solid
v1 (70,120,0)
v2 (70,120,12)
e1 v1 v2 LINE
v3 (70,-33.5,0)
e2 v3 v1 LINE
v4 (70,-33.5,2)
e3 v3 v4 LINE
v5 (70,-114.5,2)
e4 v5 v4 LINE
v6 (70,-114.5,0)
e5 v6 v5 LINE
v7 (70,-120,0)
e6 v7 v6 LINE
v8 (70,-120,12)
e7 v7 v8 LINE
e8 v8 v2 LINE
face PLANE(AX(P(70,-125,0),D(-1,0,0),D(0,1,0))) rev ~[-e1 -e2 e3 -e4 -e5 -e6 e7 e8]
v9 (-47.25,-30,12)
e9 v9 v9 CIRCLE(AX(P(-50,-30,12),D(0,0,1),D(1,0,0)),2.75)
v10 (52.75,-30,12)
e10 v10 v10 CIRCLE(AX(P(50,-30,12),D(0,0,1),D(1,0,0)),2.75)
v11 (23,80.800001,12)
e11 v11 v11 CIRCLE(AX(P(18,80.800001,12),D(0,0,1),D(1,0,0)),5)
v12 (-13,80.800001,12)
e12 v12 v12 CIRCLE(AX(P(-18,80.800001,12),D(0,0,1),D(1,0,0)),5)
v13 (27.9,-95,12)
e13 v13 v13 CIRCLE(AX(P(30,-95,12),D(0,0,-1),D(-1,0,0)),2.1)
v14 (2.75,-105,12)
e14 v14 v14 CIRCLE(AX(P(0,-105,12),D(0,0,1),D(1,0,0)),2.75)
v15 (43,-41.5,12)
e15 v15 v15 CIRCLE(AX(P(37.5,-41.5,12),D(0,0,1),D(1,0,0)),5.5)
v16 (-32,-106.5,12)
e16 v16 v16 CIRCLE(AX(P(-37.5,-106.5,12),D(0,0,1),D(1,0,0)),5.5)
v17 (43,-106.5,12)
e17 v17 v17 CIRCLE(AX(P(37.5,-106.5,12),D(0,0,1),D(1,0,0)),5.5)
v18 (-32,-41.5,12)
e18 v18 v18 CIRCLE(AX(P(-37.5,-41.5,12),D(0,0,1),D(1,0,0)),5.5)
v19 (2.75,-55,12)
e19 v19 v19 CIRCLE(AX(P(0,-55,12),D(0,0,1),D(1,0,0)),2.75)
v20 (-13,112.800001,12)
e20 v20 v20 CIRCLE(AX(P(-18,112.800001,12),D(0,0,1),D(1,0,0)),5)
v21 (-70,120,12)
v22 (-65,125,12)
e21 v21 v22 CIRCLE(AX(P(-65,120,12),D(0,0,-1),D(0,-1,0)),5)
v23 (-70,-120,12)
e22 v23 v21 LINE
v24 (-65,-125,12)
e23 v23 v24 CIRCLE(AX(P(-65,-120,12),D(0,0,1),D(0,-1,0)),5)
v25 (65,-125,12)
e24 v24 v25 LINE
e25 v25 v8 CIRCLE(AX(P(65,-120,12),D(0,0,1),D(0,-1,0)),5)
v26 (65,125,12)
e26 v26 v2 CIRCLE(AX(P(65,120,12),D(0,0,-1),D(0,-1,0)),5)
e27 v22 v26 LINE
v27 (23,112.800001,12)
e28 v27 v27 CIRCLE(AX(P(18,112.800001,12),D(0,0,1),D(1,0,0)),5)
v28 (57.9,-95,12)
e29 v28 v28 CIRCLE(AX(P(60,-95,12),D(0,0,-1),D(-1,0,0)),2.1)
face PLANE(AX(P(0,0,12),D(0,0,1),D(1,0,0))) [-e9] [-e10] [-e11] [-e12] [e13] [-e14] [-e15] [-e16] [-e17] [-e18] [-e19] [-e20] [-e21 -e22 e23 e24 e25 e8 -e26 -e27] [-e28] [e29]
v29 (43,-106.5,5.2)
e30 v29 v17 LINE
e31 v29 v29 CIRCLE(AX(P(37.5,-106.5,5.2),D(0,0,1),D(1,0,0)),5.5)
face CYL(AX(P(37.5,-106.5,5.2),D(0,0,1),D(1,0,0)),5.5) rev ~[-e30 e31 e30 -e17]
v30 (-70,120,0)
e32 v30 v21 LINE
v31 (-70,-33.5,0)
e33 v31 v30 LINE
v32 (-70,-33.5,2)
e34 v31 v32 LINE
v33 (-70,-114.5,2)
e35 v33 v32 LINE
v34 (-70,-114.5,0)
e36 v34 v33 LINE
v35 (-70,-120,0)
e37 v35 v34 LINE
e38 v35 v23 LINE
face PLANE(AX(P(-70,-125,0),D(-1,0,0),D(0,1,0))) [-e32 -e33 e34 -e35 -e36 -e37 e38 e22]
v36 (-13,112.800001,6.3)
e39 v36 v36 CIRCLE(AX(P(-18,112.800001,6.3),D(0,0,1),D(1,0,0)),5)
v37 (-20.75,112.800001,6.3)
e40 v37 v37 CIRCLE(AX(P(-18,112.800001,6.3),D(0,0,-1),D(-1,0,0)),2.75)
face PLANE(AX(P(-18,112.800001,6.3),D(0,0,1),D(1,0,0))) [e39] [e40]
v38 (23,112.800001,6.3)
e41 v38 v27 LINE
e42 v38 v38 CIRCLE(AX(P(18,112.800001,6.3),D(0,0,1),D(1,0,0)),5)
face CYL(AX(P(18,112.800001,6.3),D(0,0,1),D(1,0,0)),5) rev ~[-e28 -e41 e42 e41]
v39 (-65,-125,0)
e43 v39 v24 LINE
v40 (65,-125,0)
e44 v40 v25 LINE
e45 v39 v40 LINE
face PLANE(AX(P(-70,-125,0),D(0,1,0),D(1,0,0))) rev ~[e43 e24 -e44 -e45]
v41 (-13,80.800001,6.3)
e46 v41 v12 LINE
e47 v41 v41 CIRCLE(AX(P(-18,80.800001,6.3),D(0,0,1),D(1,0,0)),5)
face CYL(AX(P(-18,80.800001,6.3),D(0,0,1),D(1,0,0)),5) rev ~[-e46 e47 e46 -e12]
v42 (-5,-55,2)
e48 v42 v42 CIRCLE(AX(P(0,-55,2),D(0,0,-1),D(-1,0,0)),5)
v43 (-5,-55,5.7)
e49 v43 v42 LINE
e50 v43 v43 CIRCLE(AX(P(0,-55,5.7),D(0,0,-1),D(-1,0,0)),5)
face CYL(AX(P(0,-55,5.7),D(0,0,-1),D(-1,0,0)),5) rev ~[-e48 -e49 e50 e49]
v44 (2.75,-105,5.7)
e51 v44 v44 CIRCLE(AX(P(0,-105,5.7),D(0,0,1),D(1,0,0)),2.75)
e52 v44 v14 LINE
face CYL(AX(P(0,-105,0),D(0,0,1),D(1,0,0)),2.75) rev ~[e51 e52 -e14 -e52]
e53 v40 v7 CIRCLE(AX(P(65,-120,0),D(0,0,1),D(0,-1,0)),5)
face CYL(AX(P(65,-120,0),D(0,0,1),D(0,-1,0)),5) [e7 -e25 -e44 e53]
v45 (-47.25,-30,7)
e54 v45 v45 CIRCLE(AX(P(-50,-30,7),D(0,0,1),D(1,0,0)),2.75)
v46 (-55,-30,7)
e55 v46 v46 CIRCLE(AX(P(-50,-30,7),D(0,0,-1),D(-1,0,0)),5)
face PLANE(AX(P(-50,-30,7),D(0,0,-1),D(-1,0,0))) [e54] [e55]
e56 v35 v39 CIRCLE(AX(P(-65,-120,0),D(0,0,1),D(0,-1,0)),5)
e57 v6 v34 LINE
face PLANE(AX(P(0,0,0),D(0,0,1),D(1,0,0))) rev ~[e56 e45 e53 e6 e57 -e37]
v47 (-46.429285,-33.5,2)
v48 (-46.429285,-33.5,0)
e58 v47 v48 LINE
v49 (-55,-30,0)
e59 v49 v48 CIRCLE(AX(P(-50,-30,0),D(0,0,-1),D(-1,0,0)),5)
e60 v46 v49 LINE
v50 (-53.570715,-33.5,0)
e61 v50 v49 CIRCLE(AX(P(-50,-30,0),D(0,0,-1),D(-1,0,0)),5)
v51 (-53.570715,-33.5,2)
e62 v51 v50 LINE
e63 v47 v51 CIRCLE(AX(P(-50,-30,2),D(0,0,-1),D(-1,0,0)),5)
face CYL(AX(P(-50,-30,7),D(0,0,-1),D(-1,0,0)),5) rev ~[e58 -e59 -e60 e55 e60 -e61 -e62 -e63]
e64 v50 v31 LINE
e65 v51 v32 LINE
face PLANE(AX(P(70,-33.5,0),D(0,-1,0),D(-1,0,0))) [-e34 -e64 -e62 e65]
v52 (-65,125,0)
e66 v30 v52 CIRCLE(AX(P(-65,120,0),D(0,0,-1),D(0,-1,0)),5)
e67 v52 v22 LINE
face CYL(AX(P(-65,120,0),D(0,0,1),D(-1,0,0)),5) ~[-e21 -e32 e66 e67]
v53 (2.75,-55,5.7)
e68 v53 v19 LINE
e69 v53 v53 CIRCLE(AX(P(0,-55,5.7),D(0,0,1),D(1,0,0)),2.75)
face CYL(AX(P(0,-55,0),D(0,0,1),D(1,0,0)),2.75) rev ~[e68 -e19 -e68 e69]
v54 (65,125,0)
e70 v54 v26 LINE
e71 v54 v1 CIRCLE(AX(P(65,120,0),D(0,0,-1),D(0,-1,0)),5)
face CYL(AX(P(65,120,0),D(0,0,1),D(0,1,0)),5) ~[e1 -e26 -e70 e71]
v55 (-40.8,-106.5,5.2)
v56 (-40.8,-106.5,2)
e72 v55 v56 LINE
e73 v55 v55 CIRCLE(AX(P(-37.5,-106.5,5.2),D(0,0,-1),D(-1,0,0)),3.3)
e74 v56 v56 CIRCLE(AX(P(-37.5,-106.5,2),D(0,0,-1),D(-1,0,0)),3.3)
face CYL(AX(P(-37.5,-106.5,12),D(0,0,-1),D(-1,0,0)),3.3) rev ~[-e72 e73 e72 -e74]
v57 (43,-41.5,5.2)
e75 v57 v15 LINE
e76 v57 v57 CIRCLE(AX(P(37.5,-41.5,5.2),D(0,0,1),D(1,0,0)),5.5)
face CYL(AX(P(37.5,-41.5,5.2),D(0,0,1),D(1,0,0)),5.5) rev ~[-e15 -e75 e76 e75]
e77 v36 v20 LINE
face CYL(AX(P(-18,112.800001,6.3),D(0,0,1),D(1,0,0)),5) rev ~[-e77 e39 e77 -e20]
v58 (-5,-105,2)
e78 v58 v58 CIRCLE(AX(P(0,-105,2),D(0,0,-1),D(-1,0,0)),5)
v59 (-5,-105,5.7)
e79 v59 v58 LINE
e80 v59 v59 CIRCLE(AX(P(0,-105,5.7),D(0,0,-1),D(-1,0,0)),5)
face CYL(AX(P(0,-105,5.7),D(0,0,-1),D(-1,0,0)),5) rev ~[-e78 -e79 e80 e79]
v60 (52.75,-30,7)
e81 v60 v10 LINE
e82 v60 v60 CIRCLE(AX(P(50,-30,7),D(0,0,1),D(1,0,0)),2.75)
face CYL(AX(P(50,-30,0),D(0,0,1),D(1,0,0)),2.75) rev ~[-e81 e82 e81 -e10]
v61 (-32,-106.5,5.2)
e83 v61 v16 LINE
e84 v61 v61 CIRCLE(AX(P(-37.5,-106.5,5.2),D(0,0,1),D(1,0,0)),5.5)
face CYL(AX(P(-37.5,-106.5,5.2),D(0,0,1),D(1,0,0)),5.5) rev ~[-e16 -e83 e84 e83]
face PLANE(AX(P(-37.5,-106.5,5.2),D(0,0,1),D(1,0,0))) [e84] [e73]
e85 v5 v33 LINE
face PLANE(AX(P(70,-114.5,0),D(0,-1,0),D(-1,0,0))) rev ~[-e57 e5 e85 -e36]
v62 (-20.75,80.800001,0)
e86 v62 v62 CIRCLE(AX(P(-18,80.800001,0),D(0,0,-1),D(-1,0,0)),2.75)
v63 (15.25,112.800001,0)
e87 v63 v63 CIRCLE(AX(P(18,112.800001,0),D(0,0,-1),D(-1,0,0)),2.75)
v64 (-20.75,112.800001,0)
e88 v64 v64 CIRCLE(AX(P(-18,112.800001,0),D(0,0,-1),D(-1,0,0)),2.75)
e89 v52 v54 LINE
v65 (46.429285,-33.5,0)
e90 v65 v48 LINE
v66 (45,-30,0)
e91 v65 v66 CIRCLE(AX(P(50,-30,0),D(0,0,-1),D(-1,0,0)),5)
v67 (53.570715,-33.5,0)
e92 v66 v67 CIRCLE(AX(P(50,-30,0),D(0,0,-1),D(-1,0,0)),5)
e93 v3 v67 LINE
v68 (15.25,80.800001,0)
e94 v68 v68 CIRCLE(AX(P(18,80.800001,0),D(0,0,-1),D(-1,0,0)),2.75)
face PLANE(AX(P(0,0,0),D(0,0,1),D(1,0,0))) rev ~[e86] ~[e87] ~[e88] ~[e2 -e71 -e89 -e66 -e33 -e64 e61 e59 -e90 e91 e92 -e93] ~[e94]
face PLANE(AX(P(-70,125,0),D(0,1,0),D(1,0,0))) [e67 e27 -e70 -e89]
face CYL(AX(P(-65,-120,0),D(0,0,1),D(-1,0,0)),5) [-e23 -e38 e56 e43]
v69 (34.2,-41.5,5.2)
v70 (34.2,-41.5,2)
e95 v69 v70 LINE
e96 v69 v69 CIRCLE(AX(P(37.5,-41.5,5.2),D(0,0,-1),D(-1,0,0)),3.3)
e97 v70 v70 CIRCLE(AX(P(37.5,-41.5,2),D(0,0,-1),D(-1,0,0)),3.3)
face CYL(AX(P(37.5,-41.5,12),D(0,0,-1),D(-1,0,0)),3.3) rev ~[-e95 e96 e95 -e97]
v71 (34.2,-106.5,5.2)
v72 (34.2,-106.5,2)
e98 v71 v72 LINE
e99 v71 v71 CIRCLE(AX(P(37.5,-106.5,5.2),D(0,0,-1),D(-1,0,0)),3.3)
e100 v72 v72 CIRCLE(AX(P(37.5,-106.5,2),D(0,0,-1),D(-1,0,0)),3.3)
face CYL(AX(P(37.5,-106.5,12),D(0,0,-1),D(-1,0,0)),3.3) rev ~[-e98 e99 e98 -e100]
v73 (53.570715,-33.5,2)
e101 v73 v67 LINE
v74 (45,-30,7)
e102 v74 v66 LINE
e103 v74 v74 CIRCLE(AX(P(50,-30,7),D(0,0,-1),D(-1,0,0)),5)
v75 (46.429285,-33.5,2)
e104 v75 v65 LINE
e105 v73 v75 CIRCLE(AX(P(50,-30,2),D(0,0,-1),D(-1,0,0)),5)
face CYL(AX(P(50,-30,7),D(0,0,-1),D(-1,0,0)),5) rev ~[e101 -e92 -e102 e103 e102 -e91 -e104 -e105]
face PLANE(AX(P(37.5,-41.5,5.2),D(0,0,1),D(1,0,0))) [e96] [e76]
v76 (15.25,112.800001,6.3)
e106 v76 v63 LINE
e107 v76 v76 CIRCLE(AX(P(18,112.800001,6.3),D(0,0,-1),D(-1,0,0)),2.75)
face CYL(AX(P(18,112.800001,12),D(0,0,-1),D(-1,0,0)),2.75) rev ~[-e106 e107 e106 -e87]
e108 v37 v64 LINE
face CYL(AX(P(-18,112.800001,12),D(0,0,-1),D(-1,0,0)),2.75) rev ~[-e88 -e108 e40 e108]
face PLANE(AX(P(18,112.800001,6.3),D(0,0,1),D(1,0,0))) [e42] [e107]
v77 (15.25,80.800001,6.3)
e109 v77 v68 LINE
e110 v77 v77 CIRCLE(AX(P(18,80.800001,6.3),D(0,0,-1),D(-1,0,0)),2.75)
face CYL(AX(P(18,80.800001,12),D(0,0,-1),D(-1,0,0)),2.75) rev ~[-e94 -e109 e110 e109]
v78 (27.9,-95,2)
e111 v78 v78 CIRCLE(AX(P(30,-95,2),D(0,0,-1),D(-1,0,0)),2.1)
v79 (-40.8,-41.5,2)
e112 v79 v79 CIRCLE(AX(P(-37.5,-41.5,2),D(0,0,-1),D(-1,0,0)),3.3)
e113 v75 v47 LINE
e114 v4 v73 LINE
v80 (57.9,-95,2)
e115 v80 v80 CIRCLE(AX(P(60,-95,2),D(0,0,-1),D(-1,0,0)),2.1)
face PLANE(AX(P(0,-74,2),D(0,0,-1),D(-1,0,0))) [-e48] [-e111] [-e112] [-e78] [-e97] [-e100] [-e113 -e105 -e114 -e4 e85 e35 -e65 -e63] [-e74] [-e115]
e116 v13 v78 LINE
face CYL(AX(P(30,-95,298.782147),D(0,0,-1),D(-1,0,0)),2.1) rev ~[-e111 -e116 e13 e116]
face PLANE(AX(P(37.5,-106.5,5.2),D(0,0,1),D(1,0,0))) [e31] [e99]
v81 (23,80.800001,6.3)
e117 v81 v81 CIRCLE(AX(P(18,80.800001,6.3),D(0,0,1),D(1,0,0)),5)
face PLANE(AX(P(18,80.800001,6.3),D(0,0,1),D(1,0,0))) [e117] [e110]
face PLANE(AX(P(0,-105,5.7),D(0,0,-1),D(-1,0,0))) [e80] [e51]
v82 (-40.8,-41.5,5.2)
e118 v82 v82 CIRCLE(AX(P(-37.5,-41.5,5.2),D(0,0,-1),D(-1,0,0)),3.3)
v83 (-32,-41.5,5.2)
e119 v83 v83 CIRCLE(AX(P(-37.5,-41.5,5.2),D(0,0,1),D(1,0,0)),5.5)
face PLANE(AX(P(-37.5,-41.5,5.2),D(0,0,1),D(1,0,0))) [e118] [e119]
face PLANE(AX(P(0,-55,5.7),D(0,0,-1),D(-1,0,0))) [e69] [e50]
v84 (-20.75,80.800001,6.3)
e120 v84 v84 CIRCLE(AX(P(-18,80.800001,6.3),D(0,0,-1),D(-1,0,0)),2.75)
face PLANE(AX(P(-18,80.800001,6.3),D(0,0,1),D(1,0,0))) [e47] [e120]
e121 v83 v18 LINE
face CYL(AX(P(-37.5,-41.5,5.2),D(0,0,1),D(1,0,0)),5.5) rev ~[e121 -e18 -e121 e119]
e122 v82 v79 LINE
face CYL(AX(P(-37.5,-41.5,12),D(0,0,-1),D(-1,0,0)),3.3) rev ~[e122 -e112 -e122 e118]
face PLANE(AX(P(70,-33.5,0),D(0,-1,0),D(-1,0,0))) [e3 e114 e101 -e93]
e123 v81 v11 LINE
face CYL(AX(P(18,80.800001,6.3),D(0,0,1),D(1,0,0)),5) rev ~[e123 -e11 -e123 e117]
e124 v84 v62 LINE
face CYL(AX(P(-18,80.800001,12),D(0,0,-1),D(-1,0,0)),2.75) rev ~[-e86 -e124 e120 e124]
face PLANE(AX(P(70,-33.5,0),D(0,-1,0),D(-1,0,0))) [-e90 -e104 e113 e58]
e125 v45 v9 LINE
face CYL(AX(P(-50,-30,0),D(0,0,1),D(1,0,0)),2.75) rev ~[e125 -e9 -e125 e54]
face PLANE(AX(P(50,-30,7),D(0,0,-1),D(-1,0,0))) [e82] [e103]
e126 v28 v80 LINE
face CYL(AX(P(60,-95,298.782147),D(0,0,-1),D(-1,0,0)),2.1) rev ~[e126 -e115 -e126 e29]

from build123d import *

# Parameters (mm, degrees)
SKETCH_1_W                = 140
SKETCH_1_H                = 250
EXTRUDE_1_DEPTH           = 12
HOLE_WIZARD_1_D           = 5.5
HOLE_WIZARD_1_DEPTH       = 15
HOLE_WIZARD_1_CBORE_D     = 10
HOLE_WIZARD_1_CBORE_DEPTH = 5.7
HOLE_WIZARD_1_TIP         = 1.652366702
HOLE_WIZARD_2_D           = 6.6
HOLE_WIZARD_2_DEPTH       = 15
HOLE_WIZARD_2_CBORE_D     = 11
HOLE_WIZARD_2_CBORE_DEPTH = 6.8
HOLE_WIZARD_2_TIP         = 1.982840043
HOLE_WIZARD_3_D           = 5.5
HOLE_WIZARD_3_DEPTH       = 14.4
HOLE_WIZARD_3_CBORE_D     = 10
HOLE_WIZARD_3_CBORE_DEPTH = 5.7
HOLE_WIZARD_3_TIP         = 1.652366702
SKETCH_8_W                = 140
SKETCH_8_H                = 81
CUT_EXTRUDE_1_DEPTH       = 2
HOLE_WIZARD_0_D           = 5.5
HOLE_WIZARD_0_CBORE_D     = 10
HOLE_WIZARD_0_CBORE_DEPTH = 7
HOLE_WIZARD_M5_1_D        = 4.2
FILLET_1_R                = 5


with BuildPart() as part:
    # 草图1 → 凸台-拉伸1 (new body)
    with BuildSketch(Plane.XY):
        Rectangle(SKETCH_1_W, SKETCH_1_H)
    extrude(amount=EXTRUDE_1_DEPTH)

    # 打孔尺寸(%根据)内六角圆柱头螺钉的类型1
    with Locations(Plane.XY.offset(12)):
        with Locations((-18, 112.800000705), (-18, 80.800000705), (18, 80.800000705), (18, 112.800000705)):
            CounterBoreHole(HOLE_WIZARD_1_D / 2, HOLE_WIZARD_1_CBORE_D / 2, HOLE_WIZARD_1_CBORE_DEPTH, depth=HOLE_WIZARD_1_DEPTH)
            with Locations((0, 0, -(HOLE_WIZARD_1_DEPTH + HOLE_WIZARD_1_TIP / 2))):  # 118° drill point
                Cone(0, HOLE_WIZARD_1_D / 2, HOLE_WIZARD_1_TIP, mode=Mode.SUBTRACT)

    # 打孔尺寸(%根据)内六角圆柱头螺钉的类型2
    with Locations(Plane.XY.offset(12)):
        with Locations((37.5, -106.499999647), (-37.5, -106.499999647), (-37.5, -41.499999647), (37.5, -41.499999647)):
            CounterBoreHole(HOLE_WIZARD_2_D / 2, HOLE_WIZARD_2_CBORE_D / 2, HOLE_WIZARD_2_CBORE_DEPTH, depth=HOLE_WIZARD_2_DEPTH)
            with Locations((0, 0, -(HOLE_WIZARD_2_DEPTH + HOLE_WIZARD_2_TIP / 2))):  # 118° drill point
                Cone(0, HOLE_WIZARD_2_D / 2, HOLE_WIZARD_2_TIP, mode=Mode.SUBTRACT)

    # 打孔尺寸(%根据)内六角圆柱头螺钉的类型3
    with Locations(Plane(origin=(0, 0, 0), x_dir=(-1, 0, 0), z_dir=(0, 0, -1))):
        with Locations((0, -105), (0, -55)):
            CounterBoreHole(HOLE_WIZARD_3_D / 2, HOLE_WIZARD_3_CBORE_D / 2, HOLE_WIZARD_3_CBORE_DEPTH, depth=HOLE_WIZARD_3_DEPTH)
            with Locations((0, 0, -(HOLE_WIZARD_3_DEPTH + HOLE_WIZARD_3_TIP / 2))):  # 118° drill point
                Cone(0, HOLE_WIZARD_3_D / 2, HOLE_WIZARD_3_TIP, mode=Mode.SUBTRACT)

    # 草图8 → 切除-拉伸1 (cut)
    with BuildSketch(Plane(origin=(0, 0, 0), x_dir=(-1, 0, 0), z_dir=(0, 0, -1))):
        with Locations((0, -73.999999647)):
            Rectangle(SKETCH_8_W, SKETCH_8_H)
    extrude(amount=-CUT_EXTRUDE_1_DEPTH, mode=Mode.SUBTRACT)

    # 打孔尺寸(%根据)内六角圆柱头螺钉的类型0 (through all)
    with Locations(Plane(origin=(0, 0, 0), x_dir=(-1, 0, 0), z_dir=(0, 0, -1))):
        with Locations((-50, -30), (50, -30)):
            CounterBoreHole(HOLE_WIZARD_0_D / 2, HOLE_WIZARD_0_CBORE_D / 2, HOLE_WIZARD_0_CBORE_DEPTH)

    # M5 螺纹孔1 (through all)
    with Locations(Plane.XY.offset(12)):
        with Locations((30, -95), (60, -95)):
            Hole(HOLE_WIZARD_M5_1_D / 2)

    # 圆角1
    fillet_1_edges = [part.edges().sort_by_distance(p)[0] for p in [
        (-70, 125, 6),
        (70, 125, 6),
        (70, -125, 6),
        (-70, -125, 6),
    ]]
    fillet(fillet_1_edges, radius=FILLET_1_R)


solid = part.part
